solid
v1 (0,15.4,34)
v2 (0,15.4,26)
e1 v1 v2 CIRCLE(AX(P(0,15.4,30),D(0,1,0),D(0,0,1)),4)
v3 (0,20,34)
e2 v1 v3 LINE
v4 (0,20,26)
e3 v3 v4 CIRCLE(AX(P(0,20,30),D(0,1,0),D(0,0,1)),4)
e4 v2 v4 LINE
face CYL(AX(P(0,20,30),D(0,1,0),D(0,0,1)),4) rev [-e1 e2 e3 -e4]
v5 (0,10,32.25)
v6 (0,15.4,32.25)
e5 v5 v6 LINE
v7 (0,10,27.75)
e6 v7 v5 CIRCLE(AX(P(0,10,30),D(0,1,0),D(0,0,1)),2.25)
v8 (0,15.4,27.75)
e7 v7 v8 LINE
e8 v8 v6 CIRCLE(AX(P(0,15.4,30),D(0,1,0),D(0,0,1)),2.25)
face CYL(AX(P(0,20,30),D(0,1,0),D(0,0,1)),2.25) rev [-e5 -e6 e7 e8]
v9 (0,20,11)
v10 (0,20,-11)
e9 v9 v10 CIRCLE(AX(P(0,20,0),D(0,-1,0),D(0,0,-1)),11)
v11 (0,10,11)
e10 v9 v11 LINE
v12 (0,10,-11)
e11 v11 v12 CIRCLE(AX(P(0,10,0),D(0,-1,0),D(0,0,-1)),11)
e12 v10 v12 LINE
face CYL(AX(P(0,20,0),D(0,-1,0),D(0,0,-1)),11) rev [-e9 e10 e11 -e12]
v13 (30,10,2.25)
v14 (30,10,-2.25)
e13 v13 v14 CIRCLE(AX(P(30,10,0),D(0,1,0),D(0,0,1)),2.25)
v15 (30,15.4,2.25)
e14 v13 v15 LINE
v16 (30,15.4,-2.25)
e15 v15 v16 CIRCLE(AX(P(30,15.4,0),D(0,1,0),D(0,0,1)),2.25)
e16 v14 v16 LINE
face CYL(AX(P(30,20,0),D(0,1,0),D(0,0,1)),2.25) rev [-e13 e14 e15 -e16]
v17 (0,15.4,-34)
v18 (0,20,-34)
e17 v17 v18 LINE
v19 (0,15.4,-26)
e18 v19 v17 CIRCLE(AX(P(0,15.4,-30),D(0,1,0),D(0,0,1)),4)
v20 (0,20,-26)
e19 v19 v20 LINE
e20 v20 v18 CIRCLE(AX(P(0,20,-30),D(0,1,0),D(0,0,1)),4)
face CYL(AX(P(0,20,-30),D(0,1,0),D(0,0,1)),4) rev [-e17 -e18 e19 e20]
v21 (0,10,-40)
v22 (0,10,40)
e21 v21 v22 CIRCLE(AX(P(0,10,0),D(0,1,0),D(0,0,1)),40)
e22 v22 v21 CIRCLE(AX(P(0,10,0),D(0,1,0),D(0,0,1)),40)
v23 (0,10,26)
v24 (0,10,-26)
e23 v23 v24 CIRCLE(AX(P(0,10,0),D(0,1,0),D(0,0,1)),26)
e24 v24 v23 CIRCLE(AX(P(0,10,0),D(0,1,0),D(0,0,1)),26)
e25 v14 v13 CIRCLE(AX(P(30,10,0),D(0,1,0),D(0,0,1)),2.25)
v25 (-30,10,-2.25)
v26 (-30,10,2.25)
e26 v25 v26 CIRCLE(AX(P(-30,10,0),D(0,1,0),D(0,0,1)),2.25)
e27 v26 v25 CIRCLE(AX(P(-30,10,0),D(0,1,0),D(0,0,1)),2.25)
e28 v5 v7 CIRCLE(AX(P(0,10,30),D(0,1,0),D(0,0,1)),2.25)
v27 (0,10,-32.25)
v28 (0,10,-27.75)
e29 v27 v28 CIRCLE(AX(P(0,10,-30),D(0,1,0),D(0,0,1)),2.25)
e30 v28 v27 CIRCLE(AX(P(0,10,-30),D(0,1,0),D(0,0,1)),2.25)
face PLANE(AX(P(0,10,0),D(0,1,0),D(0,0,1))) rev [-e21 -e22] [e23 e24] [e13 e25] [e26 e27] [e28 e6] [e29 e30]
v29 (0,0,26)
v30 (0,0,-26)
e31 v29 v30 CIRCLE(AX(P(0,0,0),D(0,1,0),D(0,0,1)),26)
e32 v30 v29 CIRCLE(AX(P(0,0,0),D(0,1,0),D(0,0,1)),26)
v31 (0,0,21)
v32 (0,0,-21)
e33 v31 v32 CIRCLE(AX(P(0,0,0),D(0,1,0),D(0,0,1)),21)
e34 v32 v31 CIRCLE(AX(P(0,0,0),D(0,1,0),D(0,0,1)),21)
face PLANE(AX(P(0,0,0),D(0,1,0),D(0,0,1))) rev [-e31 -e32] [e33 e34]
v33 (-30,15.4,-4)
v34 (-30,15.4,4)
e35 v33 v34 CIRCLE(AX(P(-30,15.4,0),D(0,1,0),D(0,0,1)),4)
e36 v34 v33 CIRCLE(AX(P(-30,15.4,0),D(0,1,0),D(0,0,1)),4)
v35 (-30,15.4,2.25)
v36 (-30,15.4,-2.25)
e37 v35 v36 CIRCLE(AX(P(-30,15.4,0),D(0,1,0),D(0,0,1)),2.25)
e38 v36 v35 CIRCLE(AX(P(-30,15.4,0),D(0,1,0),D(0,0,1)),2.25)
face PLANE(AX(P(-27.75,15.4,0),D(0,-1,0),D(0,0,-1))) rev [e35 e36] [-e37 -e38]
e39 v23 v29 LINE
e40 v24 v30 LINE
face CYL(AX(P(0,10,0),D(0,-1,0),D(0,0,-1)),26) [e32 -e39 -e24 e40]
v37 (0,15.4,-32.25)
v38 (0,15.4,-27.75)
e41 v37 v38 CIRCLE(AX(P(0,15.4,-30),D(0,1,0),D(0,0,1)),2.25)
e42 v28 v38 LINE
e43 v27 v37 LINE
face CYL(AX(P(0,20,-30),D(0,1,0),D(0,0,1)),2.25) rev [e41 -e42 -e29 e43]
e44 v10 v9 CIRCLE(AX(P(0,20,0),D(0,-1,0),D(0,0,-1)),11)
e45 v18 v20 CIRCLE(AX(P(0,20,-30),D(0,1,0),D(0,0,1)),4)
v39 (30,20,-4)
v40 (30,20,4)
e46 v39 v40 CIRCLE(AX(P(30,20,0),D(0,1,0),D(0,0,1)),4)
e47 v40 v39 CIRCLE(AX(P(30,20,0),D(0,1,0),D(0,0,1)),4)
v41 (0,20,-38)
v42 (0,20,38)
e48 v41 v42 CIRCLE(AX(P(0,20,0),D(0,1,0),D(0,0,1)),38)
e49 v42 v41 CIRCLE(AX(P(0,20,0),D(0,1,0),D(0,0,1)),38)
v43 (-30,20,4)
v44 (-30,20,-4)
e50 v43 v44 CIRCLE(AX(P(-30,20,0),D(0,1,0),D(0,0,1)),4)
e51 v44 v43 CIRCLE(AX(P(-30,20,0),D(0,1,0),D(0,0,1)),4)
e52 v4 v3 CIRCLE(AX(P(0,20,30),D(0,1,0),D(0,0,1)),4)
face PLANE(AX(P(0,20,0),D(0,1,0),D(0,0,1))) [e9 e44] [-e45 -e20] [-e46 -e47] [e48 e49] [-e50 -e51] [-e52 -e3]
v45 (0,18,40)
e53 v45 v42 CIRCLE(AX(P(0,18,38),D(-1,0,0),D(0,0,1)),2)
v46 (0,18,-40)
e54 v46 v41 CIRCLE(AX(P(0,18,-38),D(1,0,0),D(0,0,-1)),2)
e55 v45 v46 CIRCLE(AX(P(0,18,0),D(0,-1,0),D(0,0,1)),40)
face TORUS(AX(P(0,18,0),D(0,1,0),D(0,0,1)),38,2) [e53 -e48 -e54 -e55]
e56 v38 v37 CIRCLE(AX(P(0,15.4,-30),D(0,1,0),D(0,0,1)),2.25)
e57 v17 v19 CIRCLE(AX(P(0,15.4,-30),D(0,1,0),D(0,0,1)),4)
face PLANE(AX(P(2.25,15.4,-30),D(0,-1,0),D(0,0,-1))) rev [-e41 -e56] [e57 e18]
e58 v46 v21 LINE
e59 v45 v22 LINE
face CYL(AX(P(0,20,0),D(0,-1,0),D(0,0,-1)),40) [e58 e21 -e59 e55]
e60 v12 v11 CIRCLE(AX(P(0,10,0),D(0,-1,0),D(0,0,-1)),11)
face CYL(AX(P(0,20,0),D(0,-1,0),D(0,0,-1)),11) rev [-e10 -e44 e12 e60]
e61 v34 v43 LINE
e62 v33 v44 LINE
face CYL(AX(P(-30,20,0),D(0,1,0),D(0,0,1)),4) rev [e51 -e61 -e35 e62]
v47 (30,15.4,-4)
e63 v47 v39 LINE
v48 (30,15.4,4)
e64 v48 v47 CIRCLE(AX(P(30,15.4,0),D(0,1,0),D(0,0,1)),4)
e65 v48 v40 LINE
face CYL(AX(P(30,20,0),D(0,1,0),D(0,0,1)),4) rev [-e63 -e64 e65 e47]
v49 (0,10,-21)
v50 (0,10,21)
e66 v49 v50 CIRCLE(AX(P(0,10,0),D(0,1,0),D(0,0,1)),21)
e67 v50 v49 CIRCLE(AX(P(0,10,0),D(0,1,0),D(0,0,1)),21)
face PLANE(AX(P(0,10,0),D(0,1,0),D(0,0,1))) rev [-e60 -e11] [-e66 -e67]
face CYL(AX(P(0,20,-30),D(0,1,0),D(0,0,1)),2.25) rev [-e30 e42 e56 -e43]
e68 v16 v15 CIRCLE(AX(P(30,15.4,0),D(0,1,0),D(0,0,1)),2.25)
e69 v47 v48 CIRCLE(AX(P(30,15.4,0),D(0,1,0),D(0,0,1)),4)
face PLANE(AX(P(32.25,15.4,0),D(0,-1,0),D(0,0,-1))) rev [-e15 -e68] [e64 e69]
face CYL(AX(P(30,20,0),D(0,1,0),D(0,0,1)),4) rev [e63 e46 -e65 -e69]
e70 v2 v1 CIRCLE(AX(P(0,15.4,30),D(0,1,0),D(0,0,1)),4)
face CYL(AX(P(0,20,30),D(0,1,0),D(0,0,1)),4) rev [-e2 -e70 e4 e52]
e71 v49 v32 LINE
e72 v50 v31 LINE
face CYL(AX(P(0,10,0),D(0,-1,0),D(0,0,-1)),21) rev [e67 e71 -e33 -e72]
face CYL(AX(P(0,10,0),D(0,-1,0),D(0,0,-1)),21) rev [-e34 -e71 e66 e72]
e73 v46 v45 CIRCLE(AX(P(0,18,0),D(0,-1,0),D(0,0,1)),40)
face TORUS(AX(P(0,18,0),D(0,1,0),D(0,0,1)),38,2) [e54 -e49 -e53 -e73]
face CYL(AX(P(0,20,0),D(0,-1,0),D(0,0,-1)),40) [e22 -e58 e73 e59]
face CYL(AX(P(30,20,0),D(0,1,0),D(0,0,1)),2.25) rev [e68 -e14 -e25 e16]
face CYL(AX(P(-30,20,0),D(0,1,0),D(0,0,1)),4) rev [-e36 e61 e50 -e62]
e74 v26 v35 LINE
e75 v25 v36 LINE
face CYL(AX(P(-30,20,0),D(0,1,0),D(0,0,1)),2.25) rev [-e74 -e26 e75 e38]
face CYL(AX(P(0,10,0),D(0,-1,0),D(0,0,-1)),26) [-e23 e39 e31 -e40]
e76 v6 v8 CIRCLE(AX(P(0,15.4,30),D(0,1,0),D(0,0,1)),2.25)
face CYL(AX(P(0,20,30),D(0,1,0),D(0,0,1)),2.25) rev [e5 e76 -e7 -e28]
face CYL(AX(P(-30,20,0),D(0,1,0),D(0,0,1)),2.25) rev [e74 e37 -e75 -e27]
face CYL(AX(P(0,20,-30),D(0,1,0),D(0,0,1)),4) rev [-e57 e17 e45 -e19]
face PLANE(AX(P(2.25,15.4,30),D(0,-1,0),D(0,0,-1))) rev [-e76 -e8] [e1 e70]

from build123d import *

# Parameters (mm, degrees)
SKETCH1_R                                          = 26
SKETCH1_R_2                                        = 21
BOSS_EXTRUDE1_DEPTH                                = 10
SKETCH2_R                                          = 40
BOSS_EXTRUDE2_DEPTH                                = 10
SKETCH3_R                                          = 11
CUT_EXTRUDE1_DEPTH                                 = 10
FILLET1_R                                          = 2
HOLE_SIZE_BASED_HEX_SOCKET_HEAD_CAP_SC_D           = 4.5
HOLE_SIZE_BASED_HEX_SOCKET_HEAD_CAP_SC_CBORE_D     = 8
HOLE_SIZE_BASED_HEX_SOCKET_HEAD_CAP_SC_CBORE_DEPTH = 4.6
CIRPATTERN1_COUNT                                  = 4


with BuildPart() as part:
    # Sketch1 → Boss-Extrude1 (new body)
    with BuildSketch(Plane(origin=(0, 0, 0), x_dir=(1, 0, 0), z_dir=(0, 1, 0))):
        with Locations(Location((0, 0, 0), (0, 0, 270))):
            Circle(SKETCH1_R)
        with Locations(Location((0, 0, 0), (0, 0, 270))):
            Circle(SKETCH1_R_2, mode=Mode.SUBTRACT)
    extrude(amount=BOSS_EXTRUDE1_DEPTH)

    # Sketch2 → Boss-Extrude2 (add)
    with BuildSketch(Plane(origin=(0, 10, 0), x_dir=(1, 0, 0), z_dir=(0, 1, 0))):
        with Locations(Location((0, 0, 0), (0, 0, 270))):
            Circle(SKETCH2_R)
    extrude(amount=BOSS_EXTRUDE2_DEPTH)

    # Sketch3 → Cut-Extrude1 (cut)
    with BuildSketch(Plane.XZ.offset(-10)):
        with Locations(Location((0, 0, 0), (0, 0, 270))):
            Circle(SKETCH3_R)
    extrude(amount=-CUT_EXTRUDE1_DEPTH, mode=Mode.SUBTRACT)

    # Fillet1
    fillet1_edges = [part.edges().sort_by_distance(p)[0] for p in [
        (0, 20, -40),
    ]]
    fillet(fillet1_edges, radius=FILLET1_R)

    # Hole size (%based) hex socket head cap screw type 1 (through all)
    with Locations(Plane(origin=(0, 20, 0), x_dir=(1, 0, 0), z_dir=(0, 1, 0))):
        with Locations((0, 30)):
            hole_size_based_hex_socket_head_cap_sc = CounterBoreHole(HOLE_SIZE_BASED_HEX_SOCKET_HEAD_CAP_SC_D / 2, HOLE_SIZE_BASED_HEX_SOCKET_HEAD_CAP_SC_CBORE_D / 2, HOLE_SIZE_BASED_HEX_SOCKET_HEAD_CAP_SC_CBORE_DEPTH)

    # CirPattern1: Hole size (%based) hex socket head cap screw type 1 ×4 about axis
    cirpattern1_axis = Axis((0, 0, 0), (0, 1, 0))
    for i in range(1, CIRPATTERN1_COUNT):
        add(hole_size_based_hex_socket_head_cap_sc.rotate(cirpattern1_axis, i * 360 / CIRPATTERN1_COUNT), mode=Mode.SUBTRACT)


solid = part.part
